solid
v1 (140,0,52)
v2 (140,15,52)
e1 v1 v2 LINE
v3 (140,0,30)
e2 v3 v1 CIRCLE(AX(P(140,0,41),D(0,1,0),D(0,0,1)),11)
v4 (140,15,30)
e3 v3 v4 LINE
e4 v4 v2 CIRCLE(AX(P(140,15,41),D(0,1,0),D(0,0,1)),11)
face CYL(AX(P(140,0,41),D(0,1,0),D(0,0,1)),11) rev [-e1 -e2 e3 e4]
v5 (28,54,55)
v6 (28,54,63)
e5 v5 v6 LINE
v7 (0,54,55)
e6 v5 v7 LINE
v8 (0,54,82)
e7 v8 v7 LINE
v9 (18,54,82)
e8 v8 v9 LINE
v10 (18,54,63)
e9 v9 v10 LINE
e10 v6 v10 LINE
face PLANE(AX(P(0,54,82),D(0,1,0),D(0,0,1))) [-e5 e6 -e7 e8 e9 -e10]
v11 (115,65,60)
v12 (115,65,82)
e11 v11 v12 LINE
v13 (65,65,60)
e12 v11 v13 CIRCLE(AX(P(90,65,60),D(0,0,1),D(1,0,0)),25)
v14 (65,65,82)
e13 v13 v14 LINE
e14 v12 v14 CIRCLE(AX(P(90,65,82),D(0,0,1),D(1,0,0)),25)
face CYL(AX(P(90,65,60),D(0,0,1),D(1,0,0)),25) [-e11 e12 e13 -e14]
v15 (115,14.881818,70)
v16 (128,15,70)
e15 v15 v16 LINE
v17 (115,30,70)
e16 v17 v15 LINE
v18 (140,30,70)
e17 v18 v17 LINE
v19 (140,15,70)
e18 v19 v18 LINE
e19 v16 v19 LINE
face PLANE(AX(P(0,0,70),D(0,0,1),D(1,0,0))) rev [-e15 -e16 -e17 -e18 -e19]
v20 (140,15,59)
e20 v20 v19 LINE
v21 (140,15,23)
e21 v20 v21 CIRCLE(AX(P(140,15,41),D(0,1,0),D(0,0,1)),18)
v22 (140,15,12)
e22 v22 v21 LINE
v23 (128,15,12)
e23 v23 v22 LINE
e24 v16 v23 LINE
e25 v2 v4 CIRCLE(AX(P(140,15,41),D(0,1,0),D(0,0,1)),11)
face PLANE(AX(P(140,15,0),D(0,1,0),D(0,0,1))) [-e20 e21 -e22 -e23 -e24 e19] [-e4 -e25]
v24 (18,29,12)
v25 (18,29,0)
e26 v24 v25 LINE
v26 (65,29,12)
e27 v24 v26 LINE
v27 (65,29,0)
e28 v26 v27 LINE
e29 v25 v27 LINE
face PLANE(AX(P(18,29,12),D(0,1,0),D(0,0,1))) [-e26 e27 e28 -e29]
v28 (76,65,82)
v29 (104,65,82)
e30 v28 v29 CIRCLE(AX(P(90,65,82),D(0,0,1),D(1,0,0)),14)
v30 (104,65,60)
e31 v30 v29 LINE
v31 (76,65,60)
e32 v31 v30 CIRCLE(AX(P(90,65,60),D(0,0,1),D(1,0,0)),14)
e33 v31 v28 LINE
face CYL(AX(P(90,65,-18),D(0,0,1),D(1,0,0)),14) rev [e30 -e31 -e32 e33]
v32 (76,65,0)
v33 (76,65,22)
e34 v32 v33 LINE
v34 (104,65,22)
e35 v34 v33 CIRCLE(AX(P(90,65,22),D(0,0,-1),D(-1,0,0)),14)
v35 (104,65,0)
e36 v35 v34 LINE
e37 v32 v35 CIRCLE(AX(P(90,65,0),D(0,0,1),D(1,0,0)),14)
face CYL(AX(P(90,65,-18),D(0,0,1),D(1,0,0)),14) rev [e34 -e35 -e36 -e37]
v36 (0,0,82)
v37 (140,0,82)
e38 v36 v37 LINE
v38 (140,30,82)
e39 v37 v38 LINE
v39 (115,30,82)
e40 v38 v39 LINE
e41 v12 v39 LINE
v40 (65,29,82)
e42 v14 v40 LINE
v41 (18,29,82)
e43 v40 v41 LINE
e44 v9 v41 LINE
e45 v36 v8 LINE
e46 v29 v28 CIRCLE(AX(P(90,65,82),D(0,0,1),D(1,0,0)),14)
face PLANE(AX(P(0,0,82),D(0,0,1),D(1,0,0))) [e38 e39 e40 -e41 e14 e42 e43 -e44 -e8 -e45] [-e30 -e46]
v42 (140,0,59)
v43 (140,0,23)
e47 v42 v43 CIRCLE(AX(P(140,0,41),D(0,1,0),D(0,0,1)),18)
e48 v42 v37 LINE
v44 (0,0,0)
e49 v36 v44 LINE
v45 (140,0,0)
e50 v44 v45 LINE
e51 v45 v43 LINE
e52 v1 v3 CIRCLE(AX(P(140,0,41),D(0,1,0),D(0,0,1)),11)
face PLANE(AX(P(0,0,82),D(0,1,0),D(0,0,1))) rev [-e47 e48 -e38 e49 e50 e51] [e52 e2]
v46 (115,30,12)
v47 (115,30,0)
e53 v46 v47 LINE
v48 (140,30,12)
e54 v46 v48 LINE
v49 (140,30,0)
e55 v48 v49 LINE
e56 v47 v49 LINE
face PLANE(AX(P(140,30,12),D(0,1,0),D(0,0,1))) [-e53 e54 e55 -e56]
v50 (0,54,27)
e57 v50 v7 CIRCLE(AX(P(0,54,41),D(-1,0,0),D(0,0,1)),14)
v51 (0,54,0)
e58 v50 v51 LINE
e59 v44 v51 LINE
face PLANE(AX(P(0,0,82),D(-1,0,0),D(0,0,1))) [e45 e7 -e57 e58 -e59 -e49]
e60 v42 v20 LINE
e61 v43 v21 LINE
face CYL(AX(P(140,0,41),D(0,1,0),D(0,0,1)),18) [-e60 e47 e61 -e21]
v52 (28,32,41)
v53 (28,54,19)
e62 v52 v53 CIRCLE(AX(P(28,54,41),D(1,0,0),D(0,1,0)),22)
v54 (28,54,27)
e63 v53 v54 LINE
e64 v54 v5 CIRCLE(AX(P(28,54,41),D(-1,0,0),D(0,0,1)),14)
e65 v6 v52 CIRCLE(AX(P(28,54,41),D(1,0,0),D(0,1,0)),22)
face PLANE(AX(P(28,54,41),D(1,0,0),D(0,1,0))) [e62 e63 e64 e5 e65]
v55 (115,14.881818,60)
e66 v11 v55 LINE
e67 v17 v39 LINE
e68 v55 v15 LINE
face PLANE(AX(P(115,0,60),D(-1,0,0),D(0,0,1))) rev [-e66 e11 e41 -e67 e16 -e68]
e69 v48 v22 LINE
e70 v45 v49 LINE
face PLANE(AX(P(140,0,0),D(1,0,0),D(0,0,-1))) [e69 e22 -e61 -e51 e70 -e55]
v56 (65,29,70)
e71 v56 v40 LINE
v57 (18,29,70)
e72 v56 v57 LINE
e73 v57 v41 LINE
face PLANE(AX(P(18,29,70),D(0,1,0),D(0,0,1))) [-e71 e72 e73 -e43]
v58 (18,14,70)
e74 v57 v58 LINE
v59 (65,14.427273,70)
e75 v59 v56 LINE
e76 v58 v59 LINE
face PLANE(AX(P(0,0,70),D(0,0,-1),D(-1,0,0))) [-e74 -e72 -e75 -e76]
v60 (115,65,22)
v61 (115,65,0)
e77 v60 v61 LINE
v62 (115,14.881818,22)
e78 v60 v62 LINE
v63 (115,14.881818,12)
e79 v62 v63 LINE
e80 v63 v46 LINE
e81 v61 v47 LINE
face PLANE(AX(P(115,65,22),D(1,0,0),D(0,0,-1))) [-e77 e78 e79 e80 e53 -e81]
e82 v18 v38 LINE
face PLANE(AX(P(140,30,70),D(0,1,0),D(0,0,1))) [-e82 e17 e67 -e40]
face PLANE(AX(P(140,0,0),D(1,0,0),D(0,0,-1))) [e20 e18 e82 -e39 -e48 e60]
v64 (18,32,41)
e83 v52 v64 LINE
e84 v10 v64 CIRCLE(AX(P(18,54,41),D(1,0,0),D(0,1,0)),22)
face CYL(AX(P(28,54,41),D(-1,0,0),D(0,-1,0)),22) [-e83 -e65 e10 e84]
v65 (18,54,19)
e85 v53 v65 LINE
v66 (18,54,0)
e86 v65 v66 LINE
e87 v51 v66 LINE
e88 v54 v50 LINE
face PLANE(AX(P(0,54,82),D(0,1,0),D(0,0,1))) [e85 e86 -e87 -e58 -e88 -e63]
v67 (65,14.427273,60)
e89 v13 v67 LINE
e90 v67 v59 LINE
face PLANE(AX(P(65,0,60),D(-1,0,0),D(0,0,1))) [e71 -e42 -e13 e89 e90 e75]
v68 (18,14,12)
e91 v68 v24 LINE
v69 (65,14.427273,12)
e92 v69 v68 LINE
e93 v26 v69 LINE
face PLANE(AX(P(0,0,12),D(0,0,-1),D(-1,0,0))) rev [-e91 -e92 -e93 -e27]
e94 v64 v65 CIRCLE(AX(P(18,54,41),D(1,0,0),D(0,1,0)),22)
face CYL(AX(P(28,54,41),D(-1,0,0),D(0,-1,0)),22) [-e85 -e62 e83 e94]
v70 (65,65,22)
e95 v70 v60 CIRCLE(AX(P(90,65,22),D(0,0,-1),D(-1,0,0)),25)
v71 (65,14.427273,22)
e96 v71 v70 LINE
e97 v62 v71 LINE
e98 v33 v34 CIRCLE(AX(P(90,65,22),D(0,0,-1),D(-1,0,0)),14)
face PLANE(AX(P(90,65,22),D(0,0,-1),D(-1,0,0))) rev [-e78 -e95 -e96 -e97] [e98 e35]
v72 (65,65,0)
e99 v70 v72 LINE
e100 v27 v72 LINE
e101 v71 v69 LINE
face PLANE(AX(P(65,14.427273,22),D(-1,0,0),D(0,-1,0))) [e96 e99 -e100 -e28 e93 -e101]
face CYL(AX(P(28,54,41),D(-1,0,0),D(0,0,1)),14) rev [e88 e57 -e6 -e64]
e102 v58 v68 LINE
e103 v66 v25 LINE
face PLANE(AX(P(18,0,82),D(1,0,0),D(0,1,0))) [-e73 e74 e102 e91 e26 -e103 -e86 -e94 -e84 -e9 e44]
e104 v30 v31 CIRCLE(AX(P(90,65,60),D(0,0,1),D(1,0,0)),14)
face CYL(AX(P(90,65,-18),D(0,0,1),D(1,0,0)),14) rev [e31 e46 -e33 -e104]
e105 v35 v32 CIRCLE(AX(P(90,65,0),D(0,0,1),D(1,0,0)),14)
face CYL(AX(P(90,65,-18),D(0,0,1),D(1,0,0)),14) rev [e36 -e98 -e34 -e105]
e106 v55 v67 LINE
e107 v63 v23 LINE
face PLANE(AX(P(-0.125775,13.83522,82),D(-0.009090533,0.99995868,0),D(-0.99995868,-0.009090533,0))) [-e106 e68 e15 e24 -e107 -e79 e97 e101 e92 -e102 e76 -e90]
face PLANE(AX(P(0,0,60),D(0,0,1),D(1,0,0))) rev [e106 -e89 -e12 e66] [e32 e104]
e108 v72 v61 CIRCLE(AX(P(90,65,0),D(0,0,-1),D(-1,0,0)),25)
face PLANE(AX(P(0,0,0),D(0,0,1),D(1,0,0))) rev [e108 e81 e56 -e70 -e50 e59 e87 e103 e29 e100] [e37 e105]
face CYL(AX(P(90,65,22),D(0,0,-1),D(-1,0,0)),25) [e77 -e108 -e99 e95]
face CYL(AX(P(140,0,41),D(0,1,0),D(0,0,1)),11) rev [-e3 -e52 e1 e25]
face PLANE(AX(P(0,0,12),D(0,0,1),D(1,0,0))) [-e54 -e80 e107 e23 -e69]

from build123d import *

# Parameters (mm, degrees)
BASE_BLOCK_DEPTH       = 82
POCKET_1_SKETCH_W      = 82
POCKET_1_SKETCH_H      = 15
POCKET_CUT_1_DEPTH     = 82
POCKET_2_SKETCH_W      = 12
POCKET_2_SKETCH_H      = 82
POCKET_CUT_2_DEPTH     = 82
PAD_SKETCH_W           = 12
PAD_SKETCH_H           = 15
FULL_WIDTH_PAD_DEPTH   = 82
LUG_1_DEPTH            = 22
LUG_START              = -22
LUG_2_DEPTH            = 22
WEB_1_DEPTH            = 12
WEB_2_DEPTH            = 12
WEB_3_DEPTH            = 12
WEB_4_DEPTH            = 12
LUG_BORE_SKETCH_R      = 14
LUG_BORE_DEPTH         = 100
EAR_BOSS_DEPTH         = 15
EAR_HOLE_SKETCH_R      = 11
EAR_HOLE_DEPTH         = 15
SIDE_BOSS_DEPTH        = 10
BEARING_SEAT_CUT_DEPTH = 28


with BuildPart() as part:
    # Base Profile Sketch → Base Block (new body)
    with BuildSketch(Plane.XY):
        Polygon((0, 15), (0, 0), (140, 0), (140, 30), (128, 30), (128, 15), (18, 14), (18, 54), (0, 54), align=None)
    extrude(amount=BASE_BLOCK_DEPTH)

    # Pocket 1 Sketch → Pocket Cut 1 (cut)
    with BuildSketch(Plane.ZY.offset(-128)):
        with Locations((41, 22.5)):
            Rectangle(POCKET_1_SKETCH_W, POCKET_1_SKETCH_H)
    extrude(amount=-POCKET_CUT_1_DEPTH, mode=Mode.SUBTRACT)

    # Pocket 2 Sketch → Pocket Cut 2 (cut)
    with BuildSketch(Plane(origin=(0, 15, 0), x_dir=(1, 0, 0), z_dir=(0, 1, 0))):
        with Locations((134, -41)):
            Rectangle(POCKET_2_SKETCH_W, POCKET_2_SKETCH_H)
    extrude(amount=-POCKET_CUT_2_DEPTH, mode=Mode.SUBTRACT)

    # Pad Sketch → Full Width Pad (add)
    with BuildSketch(Plane.XY.offset(82)):
        with Locations((134, 7.5)):
            Rectangle(PAD_SKETCH_W, PAD_SKETCH_H)
    extrude(amount=-FULL_WIDTH_PAD_DEPTH)

    # Lug 1 Sketch → Lug 1 (add)
    with BuildSketch(Plane.XY.offset(82)):
        with BuildLine():
            ThreePointArc((115, 65), (90, 90), (65, 65))
            Line((65, 65), (65, 14.427272727))
            Line((65, 14.427272727), (90, 14.654545455))
            Line((90, 14.654545455), (115, 14.881818182))
            Line((115, 14.881818182), (115, 65))
        make_face()
    extrude(amount=-LUG_1_DEPTH)

    # Lug 2 Sketch → Lug 2 (add)
    with BuildSketch(Plane(origin=(0, 0, 0), x_dir=(-1, 0, 0), z_dir=(0, 0, -1)).offset(LUG_START)):
        with BuildLine():
            Line((-115, 65), (-115, 14.881818182))
            Line((-115, 14.881818182), (-65, 14.427272727))
            Line((-65, 14.427272727), (-65, 65))
            ThreePointArc((-65, 65), (-90, 90), (-115, 65))
        make_face()
    extrude(amount=LUG_2_DEPTH)

    # Web 1 Sketch → Web 1 (add)
    with BuildSketch(Plane(origin=(0, 0, 0), x_dir=(-1, 0, 0), z_dir=(0, 0, -1))):
        Polygon((-18, 14), (-18, 29), (-65, 29), (-65, 14.427272727), align=None)
    extrude(amount=-WEB_1_DEPTH)

    # Web 2 Sketch → Web 2 (add)
    with BuildSketch(Plane(origin=(0, 0, 0), x_dir=(-1, 0, 0), z_dir=(0, 0, -1))):
        Polygon((-140, 15), (-140, 30), (-115, 30), (-115, 14.881818182), align=None)
    extrude(amount=-WEB_2_DEPTH)

    # Web 3 Sketch → Web 3 (add)
    with BuildSketch(Plane.XY.offset(82)):
        Polygon((115, 30), (115, 14.881818182), (140, 15), (140, 30), align=None)
    extrude(amount=-WEB_3_DEPTH)

    # Web 4 Sketch → Web 4 (add)
    with BuildSketch(Plane.XY.offset(82)):
        Polygon((18, 14), (18, 29), (65, 29), (65, 14.427272727), align=None)
    extrude(amount=-WEB_4_DEPTH)

    # Lug Bore Sketch → Lug Bore (cut)
    with BuildSketch(Plane.XY.offset(82)):
        with Locations((90, 65)):
            Circle(LUG_BORE_SKETCH_R)
    extrude(amount=-LUG_BORE_DEPTH, mode=Mode.SUBTRACT)

    # Ear Boss Sketch → Ear Boss (add)
    with BuildSketch(Plane(origin=(0, 15, 0), x_dir=(1, 0, 0), z_dir=(0, 1, 0))):
        with BuildLine():
            Line((140, -23), (140, -59))
            ThreePointArc((140, -59), (158, -41), (140, -23))
        make_face()
    extrude(amount=-EAR_BOSS_DEPTH)

    # Ear Hole Sketch → Ear Hole (cut)
    with BuildSketch(Plane(origin=(0, 15, 0), x_dir=(1, 0, 0), z_dir=(0, 1, 0))):
        with Locations(Location((140, -41, 0), (0, 0, 270))):
            Circle(EAR_HOLE_SKETCH_R)
    extrude(amount=-EAR_HOLE_DEPTH, mode=Mode.SUBTRACT)

    # Side Boss Sketch → Side Boss (add)
    with BuildSketch(Plane(origin=(18, 0, 0), x_dir=(0, 0, -1), z_dir=(1, 0, 0))):
        with BuildLine():
            Line((-63, 54), (-19, 54))
            ThreePointArc((-19, 54), (-41, 32), (-63, 54))
        make_face()
    extrude(amount=SIDE_BOSS_DEPTH)

    # Bearing Seat Sketch → Bearing Seat Cut (cut)
    with BuildSketch(Plane.ZY):
        with BuildLine():
            Line((27, 54), (55, 54))
            ThreePointArc((55, 54), (41, 40), (27, 54))
        make_face()
    extrude(amount=-BEARING_SEAT_CUT_DEPTH, mode=Mode.SUBTRACT)


solid = part.part
